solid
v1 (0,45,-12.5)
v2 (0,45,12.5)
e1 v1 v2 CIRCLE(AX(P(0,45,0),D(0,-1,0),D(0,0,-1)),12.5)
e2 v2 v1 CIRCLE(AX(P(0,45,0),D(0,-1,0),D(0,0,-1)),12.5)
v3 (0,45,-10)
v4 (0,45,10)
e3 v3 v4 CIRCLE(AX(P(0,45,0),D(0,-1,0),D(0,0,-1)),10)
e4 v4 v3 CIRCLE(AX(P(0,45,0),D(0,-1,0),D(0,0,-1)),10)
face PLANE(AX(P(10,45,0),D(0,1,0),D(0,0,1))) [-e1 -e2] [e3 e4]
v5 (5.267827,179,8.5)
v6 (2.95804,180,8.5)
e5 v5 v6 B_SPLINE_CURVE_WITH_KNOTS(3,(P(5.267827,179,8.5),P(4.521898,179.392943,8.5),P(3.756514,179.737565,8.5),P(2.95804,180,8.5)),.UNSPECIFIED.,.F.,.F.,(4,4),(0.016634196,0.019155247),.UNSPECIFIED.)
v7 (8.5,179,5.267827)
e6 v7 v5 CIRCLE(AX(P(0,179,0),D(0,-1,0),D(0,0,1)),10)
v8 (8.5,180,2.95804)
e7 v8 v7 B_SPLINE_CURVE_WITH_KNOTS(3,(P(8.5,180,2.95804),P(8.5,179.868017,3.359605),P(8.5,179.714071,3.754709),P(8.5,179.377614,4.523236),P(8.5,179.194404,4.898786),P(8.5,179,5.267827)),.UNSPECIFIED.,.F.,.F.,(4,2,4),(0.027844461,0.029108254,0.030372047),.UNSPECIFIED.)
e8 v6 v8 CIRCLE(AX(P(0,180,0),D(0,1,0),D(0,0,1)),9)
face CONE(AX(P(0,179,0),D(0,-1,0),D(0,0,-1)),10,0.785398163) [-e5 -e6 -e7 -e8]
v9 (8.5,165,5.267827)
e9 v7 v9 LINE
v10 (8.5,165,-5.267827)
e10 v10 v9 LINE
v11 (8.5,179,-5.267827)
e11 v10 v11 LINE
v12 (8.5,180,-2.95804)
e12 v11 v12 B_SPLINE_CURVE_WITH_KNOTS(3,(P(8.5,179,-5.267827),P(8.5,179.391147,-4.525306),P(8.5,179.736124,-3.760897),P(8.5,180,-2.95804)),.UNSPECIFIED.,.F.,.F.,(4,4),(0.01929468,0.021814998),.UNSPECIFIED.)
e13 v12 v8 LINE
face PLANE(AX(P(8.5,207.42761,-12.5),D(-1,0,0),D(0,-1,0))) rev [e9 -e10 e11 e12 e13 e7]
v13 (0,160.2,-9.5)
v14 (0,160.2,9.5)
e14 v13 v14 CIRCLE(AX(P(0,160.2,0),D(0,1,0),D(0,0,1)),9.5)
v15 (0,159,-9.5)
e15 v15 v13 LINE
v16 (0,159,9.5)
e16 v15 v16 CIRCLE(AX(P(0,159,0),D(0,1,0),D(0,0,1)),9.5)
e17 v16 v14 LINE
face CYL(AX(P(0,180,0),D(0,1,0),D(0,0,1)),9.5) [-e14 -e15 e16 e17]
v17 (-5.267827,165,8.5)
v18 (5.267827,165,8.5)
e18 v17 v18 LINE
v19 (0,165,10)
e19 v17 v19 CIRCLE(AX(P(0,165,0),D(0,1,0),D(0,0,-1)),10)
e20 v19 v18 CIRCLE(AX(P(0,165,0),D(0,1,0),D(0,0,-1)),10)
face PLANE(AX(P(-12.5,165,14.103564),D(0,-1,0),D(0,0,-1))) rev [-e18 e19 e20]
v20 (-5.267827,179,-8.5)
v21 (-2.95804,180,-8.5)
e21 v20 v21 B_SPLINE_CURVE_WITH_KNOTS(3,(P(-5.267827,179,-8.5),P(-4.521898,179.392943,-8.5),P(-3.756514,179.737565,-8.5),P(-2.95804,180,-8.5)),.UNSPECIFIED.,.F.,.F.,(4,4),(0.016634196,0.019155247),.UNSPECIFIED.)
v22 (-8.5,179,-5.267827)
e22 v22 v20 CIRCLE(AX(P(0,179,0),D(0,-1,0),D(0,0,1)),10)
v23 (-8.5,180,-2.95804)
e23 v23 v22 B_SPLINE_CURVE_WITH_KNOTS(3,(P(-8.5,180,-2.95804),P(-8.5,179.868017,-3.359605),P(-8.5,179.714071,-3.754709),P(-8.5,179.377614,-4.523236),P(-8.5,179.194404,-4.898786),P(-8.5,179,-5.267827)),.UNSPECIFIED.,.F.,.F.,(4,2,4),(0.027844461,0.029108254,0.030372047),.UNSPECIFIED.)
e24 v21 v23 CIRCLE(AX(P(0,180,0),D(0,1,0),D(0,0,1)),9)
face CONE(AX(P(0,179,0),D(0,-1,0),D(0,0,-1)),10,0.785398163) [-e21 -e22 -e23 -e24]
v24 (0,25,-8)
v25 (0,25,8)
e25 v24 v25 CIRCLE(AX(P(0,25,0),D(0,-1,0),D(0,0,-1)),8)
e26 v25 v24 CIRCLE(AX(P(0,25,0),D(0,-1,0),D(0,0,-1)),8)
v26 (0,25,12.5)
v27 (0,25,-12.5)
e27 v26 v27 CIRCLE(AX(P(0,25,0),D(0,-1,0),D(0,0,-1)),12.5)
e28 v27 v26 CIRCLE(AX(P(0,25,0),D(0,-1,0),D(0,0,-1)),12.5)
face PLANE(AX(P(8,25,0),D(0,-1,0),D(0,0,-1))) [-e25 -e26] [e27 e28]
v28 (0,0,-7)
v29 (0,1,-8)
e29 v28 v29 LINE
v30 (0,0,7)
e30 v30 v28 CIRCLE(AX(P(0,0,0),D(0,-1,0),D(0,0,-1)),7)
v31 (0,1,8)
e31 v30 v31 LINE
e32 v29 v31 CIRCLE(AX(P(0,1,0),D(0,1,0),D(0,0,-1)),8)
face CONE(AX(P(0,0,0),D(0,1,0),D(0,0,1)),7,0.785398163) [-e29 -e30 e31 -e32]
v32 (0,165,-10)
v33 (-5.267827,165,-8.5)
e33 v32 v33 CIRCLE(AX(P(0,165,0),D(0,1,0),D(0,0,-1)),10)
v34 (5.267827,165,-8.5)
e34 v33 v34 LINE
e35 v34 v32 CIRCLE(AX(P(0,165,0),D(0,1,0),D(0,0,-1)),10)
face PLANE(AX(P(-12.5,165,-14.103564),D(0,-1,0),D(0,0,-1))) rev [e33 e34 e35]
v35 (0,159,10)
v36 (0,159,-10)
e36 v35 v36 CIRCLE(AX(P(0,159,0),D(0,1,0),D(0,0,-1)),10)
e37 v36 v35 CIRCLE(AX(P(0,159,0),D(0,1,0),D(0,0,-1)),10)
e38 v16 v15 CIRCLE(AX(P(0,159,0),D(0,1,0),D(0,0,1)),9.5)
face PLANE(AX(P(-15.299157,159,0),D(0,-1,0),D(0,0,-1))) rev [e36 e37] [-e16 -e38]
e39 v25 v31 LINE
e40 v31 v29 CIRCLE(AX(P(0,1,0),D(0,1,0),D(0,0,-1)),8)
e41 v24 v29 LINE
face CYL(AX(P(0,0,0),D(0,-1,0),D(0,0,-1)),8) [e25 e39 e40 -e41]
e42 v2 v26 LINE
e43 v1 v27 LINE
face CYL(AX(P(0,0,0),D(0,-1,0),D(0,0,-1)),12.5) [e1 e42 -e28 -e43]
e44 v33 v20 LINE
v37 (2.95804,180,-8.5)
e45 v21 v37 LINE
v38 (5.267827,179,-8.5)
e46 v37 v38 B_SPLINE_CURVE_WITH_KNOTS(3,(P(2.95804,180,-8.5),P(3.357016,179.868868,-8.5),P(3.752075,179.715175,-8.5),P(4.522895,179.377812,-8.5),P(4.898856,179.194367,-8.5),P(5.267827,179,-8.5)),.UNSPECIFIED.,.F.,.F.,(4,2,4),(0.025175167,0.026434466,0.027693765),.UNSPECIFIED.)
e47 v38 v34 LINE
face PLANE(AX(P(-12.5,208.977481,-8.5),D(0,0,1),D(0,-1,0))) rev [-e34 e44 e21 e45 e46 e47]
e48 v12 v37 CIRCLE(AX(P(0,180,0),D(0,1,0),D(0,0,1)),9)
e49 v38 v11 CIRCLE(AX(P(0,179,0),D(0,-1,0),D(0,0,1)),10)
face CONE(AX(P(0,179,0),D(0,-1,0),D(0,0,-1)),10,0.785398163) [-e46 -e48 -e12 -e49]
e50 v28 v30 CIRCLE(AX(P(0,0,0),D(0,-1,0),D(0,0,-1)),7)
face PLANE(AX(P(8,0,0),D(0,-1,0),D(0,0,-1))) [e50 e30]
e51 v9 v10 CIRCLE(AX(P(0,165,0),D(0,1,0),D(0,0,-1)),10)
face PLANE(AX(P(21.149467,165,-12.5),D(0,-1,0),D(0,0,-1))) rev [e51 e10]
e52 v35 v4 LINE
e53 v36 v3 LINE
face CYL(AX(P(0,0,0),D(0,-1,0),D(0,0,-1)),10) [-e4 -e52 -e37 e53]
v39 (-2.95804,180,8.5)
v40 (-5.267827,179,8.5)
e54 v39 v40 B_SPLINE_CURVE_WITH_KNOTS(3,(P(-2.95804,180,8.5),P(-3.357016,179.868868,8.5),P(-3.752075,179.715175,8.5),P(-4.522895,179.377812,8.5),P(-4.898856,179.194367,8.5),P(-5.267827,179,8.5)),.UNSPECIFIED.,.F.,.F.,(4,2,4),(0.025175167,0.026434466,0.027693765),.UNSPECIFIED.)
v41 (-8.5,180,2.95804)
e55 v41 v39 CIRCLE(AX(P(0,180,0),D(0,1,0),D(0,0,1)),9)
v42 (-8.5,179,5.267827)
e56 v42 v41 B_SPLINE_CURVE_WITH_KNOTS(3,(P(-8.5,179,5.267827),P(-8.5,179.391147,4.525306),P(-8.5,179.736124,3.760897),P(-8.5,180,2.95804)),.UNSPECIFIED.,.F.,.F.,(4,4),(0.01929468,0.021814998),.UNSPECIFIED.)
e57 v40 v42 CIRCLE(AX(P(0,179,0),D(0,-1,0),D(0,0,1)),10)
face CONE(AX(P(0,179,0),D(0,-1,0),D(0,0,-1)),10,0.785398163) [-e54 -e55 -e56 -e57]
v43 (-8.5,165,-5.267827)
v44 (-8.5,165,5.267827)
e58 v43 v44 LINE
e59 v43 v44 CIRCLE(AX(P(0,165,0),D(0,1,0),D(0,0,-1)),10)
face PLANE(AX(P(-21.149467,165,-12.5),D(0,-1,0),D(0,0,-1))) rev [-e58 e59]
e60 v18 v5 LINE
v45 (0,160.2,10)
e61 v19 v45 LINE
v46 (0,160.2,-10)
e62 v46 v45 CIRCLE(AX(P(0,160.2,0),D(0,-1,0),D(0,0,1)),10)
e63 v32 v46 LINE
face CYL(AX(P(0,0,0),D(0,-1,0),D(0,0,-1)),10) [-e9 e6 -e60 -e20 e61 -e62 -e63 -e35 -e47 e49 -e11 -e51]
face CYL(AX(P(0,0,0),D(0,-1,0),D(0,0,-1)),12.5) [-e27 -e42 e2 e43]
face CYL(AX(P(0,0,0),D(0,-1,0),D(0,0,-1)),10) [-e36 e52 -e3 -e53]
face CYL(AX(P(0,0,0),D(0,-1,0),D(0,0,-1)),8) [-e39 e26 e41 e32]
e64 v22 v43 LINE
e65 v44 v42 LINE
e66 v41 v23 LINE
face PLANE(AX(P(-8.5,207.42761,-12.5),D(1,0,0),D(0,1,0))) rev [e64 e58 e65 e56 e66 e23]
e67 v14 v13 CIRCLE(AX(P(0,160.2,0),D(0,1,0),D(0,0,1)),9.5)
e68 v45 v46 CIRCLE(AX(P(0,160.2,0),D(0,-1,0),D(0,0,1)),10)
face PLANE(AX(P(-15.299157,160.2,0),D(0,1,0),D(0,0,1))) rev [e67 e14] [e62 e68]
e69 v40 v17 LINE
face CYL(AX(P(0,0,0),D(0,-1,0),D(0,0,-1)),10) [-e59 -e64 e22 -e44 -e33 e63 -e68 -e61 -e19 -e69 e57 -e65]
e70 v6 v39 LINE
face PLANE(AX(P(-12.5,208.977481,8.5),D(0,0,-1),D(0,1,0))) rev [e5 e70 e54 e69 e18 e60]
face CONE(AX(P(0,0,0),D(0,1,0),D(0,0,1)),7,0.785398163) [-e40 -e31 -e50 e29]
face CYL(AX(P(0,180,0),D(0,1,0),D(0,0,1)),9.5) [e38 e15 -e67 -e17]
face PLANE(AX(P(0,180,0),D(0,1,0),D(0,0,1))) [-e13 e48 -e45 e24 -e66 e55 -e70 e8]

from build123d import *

# Parameters (mm, degrees)
CHAMFER1_SIZE           = 1
SKETCH3_W               = 5.79915747
SKETCH3_H               = 1.2
CUT_EXTRUDE2_DEPTH      = 181.865972477
CUT_EXTRUDE2_DEPTH_BACK = 181.865972477
SKETCH7_W               = 12.649467172
SKETCH7_H               = 42.427609508
CUT_EXTRUDE3_DEPTH      = 181.865972477
CUT_EXTRUDE3_DEPTH_BACK = 181.865972477
SKETCH8_W               = 5.603563882
SKETCH8_H               = 43.977481417


with BuildPart() as part:
    # Sketch1 → Revolve1 (revolve)
    with BuildSketch(Plane.XY, mode=Mode.PRIVATE) as revolve1_sk:
        Polygon((0, 180), (10, 180), (10, 45), (12.5, 45), (12.5, 25), (8, 25), (8, 0), (0, 0), align=None)
    revolve(revolve1_sk.sketch.rotate(Axis((0, 0, 0), (0, 1, 0)), 90), axis=Axis((0, 0, 0), (0, 1, 0)))

    # Chamfer1
    chamfer1_edges = [part.edges().sort_by_distance(p)[0] for p in [
        (0, 0, 8),
        (0, 180, 10),
    ]]
    chamfer(chamfer1_edges, length=CHAMFER1_SIZE)

    # Sketch3 → Cut-Revolve1 (revolve, cut)
    with BuildSketch(Plane.XY, mode=Mode.PRIVATE) as cut_revolve1_sk:
        with Locations((-12.399578735, 159.6)):
            Rectangle(SKETCH3_W, SKETCH3_H)
    revolve(cut_revolve1_sk.sketch.rotate(Axis((0, 180, 0), (0, -1, 0)), 270), axis=Axis((0, 180, 0), (0, -1, 0)), mode=Mode.SUBTRACT)

    # Sketch7 → Cut-Extrude2 (cut, two sides: drawn at the far end of the back side and taken through both)
    with BuildSketch(Plane.XY.offset(-CUT_EXTRUDE2_DEPTH_BACK)):
        with Locations((-14.824733586, 186.213804754)):
            Rectangle(SKETCH7_W, SKETCH7_H)
        with Locations((14.824733586, 186.213804754)):
            Rectangle(SKETCH7_W, SKETCH7_H)
    extrude(amount=CUT_EXTRUDE2_DEPTH + CUT_EXTRUDE2_DEPTH_BACK, mode=Mode.SUBTRACT)

    # Sketch8 → Cut-Extrude3 (cut, two sides: drawn at the far end of the back side and taken through both)
    with BuildSketch(Plane(origin=(0, 0, 0), x_dir=(0, 0, -1), z_dir=(1, 0, 0)).offset(-CUT_EXTRUDE3_DEPTH_BACK)):
        with Locations((-11.301781941, 186.988740709)):
            Rectangle(SKETCH8_W, SKETCH8_H)
        with Locations((11.301781941, 186.988740709)):
            Rectangle(SKETCH8_W, SKETCH8_H)
    extrude(amount=CUT_EXTRUDE3_DEPTH + CUT_EXTRUDE3_DEPTH_BACK, mode=Mode.SUBTRACT)


solid = part.part
